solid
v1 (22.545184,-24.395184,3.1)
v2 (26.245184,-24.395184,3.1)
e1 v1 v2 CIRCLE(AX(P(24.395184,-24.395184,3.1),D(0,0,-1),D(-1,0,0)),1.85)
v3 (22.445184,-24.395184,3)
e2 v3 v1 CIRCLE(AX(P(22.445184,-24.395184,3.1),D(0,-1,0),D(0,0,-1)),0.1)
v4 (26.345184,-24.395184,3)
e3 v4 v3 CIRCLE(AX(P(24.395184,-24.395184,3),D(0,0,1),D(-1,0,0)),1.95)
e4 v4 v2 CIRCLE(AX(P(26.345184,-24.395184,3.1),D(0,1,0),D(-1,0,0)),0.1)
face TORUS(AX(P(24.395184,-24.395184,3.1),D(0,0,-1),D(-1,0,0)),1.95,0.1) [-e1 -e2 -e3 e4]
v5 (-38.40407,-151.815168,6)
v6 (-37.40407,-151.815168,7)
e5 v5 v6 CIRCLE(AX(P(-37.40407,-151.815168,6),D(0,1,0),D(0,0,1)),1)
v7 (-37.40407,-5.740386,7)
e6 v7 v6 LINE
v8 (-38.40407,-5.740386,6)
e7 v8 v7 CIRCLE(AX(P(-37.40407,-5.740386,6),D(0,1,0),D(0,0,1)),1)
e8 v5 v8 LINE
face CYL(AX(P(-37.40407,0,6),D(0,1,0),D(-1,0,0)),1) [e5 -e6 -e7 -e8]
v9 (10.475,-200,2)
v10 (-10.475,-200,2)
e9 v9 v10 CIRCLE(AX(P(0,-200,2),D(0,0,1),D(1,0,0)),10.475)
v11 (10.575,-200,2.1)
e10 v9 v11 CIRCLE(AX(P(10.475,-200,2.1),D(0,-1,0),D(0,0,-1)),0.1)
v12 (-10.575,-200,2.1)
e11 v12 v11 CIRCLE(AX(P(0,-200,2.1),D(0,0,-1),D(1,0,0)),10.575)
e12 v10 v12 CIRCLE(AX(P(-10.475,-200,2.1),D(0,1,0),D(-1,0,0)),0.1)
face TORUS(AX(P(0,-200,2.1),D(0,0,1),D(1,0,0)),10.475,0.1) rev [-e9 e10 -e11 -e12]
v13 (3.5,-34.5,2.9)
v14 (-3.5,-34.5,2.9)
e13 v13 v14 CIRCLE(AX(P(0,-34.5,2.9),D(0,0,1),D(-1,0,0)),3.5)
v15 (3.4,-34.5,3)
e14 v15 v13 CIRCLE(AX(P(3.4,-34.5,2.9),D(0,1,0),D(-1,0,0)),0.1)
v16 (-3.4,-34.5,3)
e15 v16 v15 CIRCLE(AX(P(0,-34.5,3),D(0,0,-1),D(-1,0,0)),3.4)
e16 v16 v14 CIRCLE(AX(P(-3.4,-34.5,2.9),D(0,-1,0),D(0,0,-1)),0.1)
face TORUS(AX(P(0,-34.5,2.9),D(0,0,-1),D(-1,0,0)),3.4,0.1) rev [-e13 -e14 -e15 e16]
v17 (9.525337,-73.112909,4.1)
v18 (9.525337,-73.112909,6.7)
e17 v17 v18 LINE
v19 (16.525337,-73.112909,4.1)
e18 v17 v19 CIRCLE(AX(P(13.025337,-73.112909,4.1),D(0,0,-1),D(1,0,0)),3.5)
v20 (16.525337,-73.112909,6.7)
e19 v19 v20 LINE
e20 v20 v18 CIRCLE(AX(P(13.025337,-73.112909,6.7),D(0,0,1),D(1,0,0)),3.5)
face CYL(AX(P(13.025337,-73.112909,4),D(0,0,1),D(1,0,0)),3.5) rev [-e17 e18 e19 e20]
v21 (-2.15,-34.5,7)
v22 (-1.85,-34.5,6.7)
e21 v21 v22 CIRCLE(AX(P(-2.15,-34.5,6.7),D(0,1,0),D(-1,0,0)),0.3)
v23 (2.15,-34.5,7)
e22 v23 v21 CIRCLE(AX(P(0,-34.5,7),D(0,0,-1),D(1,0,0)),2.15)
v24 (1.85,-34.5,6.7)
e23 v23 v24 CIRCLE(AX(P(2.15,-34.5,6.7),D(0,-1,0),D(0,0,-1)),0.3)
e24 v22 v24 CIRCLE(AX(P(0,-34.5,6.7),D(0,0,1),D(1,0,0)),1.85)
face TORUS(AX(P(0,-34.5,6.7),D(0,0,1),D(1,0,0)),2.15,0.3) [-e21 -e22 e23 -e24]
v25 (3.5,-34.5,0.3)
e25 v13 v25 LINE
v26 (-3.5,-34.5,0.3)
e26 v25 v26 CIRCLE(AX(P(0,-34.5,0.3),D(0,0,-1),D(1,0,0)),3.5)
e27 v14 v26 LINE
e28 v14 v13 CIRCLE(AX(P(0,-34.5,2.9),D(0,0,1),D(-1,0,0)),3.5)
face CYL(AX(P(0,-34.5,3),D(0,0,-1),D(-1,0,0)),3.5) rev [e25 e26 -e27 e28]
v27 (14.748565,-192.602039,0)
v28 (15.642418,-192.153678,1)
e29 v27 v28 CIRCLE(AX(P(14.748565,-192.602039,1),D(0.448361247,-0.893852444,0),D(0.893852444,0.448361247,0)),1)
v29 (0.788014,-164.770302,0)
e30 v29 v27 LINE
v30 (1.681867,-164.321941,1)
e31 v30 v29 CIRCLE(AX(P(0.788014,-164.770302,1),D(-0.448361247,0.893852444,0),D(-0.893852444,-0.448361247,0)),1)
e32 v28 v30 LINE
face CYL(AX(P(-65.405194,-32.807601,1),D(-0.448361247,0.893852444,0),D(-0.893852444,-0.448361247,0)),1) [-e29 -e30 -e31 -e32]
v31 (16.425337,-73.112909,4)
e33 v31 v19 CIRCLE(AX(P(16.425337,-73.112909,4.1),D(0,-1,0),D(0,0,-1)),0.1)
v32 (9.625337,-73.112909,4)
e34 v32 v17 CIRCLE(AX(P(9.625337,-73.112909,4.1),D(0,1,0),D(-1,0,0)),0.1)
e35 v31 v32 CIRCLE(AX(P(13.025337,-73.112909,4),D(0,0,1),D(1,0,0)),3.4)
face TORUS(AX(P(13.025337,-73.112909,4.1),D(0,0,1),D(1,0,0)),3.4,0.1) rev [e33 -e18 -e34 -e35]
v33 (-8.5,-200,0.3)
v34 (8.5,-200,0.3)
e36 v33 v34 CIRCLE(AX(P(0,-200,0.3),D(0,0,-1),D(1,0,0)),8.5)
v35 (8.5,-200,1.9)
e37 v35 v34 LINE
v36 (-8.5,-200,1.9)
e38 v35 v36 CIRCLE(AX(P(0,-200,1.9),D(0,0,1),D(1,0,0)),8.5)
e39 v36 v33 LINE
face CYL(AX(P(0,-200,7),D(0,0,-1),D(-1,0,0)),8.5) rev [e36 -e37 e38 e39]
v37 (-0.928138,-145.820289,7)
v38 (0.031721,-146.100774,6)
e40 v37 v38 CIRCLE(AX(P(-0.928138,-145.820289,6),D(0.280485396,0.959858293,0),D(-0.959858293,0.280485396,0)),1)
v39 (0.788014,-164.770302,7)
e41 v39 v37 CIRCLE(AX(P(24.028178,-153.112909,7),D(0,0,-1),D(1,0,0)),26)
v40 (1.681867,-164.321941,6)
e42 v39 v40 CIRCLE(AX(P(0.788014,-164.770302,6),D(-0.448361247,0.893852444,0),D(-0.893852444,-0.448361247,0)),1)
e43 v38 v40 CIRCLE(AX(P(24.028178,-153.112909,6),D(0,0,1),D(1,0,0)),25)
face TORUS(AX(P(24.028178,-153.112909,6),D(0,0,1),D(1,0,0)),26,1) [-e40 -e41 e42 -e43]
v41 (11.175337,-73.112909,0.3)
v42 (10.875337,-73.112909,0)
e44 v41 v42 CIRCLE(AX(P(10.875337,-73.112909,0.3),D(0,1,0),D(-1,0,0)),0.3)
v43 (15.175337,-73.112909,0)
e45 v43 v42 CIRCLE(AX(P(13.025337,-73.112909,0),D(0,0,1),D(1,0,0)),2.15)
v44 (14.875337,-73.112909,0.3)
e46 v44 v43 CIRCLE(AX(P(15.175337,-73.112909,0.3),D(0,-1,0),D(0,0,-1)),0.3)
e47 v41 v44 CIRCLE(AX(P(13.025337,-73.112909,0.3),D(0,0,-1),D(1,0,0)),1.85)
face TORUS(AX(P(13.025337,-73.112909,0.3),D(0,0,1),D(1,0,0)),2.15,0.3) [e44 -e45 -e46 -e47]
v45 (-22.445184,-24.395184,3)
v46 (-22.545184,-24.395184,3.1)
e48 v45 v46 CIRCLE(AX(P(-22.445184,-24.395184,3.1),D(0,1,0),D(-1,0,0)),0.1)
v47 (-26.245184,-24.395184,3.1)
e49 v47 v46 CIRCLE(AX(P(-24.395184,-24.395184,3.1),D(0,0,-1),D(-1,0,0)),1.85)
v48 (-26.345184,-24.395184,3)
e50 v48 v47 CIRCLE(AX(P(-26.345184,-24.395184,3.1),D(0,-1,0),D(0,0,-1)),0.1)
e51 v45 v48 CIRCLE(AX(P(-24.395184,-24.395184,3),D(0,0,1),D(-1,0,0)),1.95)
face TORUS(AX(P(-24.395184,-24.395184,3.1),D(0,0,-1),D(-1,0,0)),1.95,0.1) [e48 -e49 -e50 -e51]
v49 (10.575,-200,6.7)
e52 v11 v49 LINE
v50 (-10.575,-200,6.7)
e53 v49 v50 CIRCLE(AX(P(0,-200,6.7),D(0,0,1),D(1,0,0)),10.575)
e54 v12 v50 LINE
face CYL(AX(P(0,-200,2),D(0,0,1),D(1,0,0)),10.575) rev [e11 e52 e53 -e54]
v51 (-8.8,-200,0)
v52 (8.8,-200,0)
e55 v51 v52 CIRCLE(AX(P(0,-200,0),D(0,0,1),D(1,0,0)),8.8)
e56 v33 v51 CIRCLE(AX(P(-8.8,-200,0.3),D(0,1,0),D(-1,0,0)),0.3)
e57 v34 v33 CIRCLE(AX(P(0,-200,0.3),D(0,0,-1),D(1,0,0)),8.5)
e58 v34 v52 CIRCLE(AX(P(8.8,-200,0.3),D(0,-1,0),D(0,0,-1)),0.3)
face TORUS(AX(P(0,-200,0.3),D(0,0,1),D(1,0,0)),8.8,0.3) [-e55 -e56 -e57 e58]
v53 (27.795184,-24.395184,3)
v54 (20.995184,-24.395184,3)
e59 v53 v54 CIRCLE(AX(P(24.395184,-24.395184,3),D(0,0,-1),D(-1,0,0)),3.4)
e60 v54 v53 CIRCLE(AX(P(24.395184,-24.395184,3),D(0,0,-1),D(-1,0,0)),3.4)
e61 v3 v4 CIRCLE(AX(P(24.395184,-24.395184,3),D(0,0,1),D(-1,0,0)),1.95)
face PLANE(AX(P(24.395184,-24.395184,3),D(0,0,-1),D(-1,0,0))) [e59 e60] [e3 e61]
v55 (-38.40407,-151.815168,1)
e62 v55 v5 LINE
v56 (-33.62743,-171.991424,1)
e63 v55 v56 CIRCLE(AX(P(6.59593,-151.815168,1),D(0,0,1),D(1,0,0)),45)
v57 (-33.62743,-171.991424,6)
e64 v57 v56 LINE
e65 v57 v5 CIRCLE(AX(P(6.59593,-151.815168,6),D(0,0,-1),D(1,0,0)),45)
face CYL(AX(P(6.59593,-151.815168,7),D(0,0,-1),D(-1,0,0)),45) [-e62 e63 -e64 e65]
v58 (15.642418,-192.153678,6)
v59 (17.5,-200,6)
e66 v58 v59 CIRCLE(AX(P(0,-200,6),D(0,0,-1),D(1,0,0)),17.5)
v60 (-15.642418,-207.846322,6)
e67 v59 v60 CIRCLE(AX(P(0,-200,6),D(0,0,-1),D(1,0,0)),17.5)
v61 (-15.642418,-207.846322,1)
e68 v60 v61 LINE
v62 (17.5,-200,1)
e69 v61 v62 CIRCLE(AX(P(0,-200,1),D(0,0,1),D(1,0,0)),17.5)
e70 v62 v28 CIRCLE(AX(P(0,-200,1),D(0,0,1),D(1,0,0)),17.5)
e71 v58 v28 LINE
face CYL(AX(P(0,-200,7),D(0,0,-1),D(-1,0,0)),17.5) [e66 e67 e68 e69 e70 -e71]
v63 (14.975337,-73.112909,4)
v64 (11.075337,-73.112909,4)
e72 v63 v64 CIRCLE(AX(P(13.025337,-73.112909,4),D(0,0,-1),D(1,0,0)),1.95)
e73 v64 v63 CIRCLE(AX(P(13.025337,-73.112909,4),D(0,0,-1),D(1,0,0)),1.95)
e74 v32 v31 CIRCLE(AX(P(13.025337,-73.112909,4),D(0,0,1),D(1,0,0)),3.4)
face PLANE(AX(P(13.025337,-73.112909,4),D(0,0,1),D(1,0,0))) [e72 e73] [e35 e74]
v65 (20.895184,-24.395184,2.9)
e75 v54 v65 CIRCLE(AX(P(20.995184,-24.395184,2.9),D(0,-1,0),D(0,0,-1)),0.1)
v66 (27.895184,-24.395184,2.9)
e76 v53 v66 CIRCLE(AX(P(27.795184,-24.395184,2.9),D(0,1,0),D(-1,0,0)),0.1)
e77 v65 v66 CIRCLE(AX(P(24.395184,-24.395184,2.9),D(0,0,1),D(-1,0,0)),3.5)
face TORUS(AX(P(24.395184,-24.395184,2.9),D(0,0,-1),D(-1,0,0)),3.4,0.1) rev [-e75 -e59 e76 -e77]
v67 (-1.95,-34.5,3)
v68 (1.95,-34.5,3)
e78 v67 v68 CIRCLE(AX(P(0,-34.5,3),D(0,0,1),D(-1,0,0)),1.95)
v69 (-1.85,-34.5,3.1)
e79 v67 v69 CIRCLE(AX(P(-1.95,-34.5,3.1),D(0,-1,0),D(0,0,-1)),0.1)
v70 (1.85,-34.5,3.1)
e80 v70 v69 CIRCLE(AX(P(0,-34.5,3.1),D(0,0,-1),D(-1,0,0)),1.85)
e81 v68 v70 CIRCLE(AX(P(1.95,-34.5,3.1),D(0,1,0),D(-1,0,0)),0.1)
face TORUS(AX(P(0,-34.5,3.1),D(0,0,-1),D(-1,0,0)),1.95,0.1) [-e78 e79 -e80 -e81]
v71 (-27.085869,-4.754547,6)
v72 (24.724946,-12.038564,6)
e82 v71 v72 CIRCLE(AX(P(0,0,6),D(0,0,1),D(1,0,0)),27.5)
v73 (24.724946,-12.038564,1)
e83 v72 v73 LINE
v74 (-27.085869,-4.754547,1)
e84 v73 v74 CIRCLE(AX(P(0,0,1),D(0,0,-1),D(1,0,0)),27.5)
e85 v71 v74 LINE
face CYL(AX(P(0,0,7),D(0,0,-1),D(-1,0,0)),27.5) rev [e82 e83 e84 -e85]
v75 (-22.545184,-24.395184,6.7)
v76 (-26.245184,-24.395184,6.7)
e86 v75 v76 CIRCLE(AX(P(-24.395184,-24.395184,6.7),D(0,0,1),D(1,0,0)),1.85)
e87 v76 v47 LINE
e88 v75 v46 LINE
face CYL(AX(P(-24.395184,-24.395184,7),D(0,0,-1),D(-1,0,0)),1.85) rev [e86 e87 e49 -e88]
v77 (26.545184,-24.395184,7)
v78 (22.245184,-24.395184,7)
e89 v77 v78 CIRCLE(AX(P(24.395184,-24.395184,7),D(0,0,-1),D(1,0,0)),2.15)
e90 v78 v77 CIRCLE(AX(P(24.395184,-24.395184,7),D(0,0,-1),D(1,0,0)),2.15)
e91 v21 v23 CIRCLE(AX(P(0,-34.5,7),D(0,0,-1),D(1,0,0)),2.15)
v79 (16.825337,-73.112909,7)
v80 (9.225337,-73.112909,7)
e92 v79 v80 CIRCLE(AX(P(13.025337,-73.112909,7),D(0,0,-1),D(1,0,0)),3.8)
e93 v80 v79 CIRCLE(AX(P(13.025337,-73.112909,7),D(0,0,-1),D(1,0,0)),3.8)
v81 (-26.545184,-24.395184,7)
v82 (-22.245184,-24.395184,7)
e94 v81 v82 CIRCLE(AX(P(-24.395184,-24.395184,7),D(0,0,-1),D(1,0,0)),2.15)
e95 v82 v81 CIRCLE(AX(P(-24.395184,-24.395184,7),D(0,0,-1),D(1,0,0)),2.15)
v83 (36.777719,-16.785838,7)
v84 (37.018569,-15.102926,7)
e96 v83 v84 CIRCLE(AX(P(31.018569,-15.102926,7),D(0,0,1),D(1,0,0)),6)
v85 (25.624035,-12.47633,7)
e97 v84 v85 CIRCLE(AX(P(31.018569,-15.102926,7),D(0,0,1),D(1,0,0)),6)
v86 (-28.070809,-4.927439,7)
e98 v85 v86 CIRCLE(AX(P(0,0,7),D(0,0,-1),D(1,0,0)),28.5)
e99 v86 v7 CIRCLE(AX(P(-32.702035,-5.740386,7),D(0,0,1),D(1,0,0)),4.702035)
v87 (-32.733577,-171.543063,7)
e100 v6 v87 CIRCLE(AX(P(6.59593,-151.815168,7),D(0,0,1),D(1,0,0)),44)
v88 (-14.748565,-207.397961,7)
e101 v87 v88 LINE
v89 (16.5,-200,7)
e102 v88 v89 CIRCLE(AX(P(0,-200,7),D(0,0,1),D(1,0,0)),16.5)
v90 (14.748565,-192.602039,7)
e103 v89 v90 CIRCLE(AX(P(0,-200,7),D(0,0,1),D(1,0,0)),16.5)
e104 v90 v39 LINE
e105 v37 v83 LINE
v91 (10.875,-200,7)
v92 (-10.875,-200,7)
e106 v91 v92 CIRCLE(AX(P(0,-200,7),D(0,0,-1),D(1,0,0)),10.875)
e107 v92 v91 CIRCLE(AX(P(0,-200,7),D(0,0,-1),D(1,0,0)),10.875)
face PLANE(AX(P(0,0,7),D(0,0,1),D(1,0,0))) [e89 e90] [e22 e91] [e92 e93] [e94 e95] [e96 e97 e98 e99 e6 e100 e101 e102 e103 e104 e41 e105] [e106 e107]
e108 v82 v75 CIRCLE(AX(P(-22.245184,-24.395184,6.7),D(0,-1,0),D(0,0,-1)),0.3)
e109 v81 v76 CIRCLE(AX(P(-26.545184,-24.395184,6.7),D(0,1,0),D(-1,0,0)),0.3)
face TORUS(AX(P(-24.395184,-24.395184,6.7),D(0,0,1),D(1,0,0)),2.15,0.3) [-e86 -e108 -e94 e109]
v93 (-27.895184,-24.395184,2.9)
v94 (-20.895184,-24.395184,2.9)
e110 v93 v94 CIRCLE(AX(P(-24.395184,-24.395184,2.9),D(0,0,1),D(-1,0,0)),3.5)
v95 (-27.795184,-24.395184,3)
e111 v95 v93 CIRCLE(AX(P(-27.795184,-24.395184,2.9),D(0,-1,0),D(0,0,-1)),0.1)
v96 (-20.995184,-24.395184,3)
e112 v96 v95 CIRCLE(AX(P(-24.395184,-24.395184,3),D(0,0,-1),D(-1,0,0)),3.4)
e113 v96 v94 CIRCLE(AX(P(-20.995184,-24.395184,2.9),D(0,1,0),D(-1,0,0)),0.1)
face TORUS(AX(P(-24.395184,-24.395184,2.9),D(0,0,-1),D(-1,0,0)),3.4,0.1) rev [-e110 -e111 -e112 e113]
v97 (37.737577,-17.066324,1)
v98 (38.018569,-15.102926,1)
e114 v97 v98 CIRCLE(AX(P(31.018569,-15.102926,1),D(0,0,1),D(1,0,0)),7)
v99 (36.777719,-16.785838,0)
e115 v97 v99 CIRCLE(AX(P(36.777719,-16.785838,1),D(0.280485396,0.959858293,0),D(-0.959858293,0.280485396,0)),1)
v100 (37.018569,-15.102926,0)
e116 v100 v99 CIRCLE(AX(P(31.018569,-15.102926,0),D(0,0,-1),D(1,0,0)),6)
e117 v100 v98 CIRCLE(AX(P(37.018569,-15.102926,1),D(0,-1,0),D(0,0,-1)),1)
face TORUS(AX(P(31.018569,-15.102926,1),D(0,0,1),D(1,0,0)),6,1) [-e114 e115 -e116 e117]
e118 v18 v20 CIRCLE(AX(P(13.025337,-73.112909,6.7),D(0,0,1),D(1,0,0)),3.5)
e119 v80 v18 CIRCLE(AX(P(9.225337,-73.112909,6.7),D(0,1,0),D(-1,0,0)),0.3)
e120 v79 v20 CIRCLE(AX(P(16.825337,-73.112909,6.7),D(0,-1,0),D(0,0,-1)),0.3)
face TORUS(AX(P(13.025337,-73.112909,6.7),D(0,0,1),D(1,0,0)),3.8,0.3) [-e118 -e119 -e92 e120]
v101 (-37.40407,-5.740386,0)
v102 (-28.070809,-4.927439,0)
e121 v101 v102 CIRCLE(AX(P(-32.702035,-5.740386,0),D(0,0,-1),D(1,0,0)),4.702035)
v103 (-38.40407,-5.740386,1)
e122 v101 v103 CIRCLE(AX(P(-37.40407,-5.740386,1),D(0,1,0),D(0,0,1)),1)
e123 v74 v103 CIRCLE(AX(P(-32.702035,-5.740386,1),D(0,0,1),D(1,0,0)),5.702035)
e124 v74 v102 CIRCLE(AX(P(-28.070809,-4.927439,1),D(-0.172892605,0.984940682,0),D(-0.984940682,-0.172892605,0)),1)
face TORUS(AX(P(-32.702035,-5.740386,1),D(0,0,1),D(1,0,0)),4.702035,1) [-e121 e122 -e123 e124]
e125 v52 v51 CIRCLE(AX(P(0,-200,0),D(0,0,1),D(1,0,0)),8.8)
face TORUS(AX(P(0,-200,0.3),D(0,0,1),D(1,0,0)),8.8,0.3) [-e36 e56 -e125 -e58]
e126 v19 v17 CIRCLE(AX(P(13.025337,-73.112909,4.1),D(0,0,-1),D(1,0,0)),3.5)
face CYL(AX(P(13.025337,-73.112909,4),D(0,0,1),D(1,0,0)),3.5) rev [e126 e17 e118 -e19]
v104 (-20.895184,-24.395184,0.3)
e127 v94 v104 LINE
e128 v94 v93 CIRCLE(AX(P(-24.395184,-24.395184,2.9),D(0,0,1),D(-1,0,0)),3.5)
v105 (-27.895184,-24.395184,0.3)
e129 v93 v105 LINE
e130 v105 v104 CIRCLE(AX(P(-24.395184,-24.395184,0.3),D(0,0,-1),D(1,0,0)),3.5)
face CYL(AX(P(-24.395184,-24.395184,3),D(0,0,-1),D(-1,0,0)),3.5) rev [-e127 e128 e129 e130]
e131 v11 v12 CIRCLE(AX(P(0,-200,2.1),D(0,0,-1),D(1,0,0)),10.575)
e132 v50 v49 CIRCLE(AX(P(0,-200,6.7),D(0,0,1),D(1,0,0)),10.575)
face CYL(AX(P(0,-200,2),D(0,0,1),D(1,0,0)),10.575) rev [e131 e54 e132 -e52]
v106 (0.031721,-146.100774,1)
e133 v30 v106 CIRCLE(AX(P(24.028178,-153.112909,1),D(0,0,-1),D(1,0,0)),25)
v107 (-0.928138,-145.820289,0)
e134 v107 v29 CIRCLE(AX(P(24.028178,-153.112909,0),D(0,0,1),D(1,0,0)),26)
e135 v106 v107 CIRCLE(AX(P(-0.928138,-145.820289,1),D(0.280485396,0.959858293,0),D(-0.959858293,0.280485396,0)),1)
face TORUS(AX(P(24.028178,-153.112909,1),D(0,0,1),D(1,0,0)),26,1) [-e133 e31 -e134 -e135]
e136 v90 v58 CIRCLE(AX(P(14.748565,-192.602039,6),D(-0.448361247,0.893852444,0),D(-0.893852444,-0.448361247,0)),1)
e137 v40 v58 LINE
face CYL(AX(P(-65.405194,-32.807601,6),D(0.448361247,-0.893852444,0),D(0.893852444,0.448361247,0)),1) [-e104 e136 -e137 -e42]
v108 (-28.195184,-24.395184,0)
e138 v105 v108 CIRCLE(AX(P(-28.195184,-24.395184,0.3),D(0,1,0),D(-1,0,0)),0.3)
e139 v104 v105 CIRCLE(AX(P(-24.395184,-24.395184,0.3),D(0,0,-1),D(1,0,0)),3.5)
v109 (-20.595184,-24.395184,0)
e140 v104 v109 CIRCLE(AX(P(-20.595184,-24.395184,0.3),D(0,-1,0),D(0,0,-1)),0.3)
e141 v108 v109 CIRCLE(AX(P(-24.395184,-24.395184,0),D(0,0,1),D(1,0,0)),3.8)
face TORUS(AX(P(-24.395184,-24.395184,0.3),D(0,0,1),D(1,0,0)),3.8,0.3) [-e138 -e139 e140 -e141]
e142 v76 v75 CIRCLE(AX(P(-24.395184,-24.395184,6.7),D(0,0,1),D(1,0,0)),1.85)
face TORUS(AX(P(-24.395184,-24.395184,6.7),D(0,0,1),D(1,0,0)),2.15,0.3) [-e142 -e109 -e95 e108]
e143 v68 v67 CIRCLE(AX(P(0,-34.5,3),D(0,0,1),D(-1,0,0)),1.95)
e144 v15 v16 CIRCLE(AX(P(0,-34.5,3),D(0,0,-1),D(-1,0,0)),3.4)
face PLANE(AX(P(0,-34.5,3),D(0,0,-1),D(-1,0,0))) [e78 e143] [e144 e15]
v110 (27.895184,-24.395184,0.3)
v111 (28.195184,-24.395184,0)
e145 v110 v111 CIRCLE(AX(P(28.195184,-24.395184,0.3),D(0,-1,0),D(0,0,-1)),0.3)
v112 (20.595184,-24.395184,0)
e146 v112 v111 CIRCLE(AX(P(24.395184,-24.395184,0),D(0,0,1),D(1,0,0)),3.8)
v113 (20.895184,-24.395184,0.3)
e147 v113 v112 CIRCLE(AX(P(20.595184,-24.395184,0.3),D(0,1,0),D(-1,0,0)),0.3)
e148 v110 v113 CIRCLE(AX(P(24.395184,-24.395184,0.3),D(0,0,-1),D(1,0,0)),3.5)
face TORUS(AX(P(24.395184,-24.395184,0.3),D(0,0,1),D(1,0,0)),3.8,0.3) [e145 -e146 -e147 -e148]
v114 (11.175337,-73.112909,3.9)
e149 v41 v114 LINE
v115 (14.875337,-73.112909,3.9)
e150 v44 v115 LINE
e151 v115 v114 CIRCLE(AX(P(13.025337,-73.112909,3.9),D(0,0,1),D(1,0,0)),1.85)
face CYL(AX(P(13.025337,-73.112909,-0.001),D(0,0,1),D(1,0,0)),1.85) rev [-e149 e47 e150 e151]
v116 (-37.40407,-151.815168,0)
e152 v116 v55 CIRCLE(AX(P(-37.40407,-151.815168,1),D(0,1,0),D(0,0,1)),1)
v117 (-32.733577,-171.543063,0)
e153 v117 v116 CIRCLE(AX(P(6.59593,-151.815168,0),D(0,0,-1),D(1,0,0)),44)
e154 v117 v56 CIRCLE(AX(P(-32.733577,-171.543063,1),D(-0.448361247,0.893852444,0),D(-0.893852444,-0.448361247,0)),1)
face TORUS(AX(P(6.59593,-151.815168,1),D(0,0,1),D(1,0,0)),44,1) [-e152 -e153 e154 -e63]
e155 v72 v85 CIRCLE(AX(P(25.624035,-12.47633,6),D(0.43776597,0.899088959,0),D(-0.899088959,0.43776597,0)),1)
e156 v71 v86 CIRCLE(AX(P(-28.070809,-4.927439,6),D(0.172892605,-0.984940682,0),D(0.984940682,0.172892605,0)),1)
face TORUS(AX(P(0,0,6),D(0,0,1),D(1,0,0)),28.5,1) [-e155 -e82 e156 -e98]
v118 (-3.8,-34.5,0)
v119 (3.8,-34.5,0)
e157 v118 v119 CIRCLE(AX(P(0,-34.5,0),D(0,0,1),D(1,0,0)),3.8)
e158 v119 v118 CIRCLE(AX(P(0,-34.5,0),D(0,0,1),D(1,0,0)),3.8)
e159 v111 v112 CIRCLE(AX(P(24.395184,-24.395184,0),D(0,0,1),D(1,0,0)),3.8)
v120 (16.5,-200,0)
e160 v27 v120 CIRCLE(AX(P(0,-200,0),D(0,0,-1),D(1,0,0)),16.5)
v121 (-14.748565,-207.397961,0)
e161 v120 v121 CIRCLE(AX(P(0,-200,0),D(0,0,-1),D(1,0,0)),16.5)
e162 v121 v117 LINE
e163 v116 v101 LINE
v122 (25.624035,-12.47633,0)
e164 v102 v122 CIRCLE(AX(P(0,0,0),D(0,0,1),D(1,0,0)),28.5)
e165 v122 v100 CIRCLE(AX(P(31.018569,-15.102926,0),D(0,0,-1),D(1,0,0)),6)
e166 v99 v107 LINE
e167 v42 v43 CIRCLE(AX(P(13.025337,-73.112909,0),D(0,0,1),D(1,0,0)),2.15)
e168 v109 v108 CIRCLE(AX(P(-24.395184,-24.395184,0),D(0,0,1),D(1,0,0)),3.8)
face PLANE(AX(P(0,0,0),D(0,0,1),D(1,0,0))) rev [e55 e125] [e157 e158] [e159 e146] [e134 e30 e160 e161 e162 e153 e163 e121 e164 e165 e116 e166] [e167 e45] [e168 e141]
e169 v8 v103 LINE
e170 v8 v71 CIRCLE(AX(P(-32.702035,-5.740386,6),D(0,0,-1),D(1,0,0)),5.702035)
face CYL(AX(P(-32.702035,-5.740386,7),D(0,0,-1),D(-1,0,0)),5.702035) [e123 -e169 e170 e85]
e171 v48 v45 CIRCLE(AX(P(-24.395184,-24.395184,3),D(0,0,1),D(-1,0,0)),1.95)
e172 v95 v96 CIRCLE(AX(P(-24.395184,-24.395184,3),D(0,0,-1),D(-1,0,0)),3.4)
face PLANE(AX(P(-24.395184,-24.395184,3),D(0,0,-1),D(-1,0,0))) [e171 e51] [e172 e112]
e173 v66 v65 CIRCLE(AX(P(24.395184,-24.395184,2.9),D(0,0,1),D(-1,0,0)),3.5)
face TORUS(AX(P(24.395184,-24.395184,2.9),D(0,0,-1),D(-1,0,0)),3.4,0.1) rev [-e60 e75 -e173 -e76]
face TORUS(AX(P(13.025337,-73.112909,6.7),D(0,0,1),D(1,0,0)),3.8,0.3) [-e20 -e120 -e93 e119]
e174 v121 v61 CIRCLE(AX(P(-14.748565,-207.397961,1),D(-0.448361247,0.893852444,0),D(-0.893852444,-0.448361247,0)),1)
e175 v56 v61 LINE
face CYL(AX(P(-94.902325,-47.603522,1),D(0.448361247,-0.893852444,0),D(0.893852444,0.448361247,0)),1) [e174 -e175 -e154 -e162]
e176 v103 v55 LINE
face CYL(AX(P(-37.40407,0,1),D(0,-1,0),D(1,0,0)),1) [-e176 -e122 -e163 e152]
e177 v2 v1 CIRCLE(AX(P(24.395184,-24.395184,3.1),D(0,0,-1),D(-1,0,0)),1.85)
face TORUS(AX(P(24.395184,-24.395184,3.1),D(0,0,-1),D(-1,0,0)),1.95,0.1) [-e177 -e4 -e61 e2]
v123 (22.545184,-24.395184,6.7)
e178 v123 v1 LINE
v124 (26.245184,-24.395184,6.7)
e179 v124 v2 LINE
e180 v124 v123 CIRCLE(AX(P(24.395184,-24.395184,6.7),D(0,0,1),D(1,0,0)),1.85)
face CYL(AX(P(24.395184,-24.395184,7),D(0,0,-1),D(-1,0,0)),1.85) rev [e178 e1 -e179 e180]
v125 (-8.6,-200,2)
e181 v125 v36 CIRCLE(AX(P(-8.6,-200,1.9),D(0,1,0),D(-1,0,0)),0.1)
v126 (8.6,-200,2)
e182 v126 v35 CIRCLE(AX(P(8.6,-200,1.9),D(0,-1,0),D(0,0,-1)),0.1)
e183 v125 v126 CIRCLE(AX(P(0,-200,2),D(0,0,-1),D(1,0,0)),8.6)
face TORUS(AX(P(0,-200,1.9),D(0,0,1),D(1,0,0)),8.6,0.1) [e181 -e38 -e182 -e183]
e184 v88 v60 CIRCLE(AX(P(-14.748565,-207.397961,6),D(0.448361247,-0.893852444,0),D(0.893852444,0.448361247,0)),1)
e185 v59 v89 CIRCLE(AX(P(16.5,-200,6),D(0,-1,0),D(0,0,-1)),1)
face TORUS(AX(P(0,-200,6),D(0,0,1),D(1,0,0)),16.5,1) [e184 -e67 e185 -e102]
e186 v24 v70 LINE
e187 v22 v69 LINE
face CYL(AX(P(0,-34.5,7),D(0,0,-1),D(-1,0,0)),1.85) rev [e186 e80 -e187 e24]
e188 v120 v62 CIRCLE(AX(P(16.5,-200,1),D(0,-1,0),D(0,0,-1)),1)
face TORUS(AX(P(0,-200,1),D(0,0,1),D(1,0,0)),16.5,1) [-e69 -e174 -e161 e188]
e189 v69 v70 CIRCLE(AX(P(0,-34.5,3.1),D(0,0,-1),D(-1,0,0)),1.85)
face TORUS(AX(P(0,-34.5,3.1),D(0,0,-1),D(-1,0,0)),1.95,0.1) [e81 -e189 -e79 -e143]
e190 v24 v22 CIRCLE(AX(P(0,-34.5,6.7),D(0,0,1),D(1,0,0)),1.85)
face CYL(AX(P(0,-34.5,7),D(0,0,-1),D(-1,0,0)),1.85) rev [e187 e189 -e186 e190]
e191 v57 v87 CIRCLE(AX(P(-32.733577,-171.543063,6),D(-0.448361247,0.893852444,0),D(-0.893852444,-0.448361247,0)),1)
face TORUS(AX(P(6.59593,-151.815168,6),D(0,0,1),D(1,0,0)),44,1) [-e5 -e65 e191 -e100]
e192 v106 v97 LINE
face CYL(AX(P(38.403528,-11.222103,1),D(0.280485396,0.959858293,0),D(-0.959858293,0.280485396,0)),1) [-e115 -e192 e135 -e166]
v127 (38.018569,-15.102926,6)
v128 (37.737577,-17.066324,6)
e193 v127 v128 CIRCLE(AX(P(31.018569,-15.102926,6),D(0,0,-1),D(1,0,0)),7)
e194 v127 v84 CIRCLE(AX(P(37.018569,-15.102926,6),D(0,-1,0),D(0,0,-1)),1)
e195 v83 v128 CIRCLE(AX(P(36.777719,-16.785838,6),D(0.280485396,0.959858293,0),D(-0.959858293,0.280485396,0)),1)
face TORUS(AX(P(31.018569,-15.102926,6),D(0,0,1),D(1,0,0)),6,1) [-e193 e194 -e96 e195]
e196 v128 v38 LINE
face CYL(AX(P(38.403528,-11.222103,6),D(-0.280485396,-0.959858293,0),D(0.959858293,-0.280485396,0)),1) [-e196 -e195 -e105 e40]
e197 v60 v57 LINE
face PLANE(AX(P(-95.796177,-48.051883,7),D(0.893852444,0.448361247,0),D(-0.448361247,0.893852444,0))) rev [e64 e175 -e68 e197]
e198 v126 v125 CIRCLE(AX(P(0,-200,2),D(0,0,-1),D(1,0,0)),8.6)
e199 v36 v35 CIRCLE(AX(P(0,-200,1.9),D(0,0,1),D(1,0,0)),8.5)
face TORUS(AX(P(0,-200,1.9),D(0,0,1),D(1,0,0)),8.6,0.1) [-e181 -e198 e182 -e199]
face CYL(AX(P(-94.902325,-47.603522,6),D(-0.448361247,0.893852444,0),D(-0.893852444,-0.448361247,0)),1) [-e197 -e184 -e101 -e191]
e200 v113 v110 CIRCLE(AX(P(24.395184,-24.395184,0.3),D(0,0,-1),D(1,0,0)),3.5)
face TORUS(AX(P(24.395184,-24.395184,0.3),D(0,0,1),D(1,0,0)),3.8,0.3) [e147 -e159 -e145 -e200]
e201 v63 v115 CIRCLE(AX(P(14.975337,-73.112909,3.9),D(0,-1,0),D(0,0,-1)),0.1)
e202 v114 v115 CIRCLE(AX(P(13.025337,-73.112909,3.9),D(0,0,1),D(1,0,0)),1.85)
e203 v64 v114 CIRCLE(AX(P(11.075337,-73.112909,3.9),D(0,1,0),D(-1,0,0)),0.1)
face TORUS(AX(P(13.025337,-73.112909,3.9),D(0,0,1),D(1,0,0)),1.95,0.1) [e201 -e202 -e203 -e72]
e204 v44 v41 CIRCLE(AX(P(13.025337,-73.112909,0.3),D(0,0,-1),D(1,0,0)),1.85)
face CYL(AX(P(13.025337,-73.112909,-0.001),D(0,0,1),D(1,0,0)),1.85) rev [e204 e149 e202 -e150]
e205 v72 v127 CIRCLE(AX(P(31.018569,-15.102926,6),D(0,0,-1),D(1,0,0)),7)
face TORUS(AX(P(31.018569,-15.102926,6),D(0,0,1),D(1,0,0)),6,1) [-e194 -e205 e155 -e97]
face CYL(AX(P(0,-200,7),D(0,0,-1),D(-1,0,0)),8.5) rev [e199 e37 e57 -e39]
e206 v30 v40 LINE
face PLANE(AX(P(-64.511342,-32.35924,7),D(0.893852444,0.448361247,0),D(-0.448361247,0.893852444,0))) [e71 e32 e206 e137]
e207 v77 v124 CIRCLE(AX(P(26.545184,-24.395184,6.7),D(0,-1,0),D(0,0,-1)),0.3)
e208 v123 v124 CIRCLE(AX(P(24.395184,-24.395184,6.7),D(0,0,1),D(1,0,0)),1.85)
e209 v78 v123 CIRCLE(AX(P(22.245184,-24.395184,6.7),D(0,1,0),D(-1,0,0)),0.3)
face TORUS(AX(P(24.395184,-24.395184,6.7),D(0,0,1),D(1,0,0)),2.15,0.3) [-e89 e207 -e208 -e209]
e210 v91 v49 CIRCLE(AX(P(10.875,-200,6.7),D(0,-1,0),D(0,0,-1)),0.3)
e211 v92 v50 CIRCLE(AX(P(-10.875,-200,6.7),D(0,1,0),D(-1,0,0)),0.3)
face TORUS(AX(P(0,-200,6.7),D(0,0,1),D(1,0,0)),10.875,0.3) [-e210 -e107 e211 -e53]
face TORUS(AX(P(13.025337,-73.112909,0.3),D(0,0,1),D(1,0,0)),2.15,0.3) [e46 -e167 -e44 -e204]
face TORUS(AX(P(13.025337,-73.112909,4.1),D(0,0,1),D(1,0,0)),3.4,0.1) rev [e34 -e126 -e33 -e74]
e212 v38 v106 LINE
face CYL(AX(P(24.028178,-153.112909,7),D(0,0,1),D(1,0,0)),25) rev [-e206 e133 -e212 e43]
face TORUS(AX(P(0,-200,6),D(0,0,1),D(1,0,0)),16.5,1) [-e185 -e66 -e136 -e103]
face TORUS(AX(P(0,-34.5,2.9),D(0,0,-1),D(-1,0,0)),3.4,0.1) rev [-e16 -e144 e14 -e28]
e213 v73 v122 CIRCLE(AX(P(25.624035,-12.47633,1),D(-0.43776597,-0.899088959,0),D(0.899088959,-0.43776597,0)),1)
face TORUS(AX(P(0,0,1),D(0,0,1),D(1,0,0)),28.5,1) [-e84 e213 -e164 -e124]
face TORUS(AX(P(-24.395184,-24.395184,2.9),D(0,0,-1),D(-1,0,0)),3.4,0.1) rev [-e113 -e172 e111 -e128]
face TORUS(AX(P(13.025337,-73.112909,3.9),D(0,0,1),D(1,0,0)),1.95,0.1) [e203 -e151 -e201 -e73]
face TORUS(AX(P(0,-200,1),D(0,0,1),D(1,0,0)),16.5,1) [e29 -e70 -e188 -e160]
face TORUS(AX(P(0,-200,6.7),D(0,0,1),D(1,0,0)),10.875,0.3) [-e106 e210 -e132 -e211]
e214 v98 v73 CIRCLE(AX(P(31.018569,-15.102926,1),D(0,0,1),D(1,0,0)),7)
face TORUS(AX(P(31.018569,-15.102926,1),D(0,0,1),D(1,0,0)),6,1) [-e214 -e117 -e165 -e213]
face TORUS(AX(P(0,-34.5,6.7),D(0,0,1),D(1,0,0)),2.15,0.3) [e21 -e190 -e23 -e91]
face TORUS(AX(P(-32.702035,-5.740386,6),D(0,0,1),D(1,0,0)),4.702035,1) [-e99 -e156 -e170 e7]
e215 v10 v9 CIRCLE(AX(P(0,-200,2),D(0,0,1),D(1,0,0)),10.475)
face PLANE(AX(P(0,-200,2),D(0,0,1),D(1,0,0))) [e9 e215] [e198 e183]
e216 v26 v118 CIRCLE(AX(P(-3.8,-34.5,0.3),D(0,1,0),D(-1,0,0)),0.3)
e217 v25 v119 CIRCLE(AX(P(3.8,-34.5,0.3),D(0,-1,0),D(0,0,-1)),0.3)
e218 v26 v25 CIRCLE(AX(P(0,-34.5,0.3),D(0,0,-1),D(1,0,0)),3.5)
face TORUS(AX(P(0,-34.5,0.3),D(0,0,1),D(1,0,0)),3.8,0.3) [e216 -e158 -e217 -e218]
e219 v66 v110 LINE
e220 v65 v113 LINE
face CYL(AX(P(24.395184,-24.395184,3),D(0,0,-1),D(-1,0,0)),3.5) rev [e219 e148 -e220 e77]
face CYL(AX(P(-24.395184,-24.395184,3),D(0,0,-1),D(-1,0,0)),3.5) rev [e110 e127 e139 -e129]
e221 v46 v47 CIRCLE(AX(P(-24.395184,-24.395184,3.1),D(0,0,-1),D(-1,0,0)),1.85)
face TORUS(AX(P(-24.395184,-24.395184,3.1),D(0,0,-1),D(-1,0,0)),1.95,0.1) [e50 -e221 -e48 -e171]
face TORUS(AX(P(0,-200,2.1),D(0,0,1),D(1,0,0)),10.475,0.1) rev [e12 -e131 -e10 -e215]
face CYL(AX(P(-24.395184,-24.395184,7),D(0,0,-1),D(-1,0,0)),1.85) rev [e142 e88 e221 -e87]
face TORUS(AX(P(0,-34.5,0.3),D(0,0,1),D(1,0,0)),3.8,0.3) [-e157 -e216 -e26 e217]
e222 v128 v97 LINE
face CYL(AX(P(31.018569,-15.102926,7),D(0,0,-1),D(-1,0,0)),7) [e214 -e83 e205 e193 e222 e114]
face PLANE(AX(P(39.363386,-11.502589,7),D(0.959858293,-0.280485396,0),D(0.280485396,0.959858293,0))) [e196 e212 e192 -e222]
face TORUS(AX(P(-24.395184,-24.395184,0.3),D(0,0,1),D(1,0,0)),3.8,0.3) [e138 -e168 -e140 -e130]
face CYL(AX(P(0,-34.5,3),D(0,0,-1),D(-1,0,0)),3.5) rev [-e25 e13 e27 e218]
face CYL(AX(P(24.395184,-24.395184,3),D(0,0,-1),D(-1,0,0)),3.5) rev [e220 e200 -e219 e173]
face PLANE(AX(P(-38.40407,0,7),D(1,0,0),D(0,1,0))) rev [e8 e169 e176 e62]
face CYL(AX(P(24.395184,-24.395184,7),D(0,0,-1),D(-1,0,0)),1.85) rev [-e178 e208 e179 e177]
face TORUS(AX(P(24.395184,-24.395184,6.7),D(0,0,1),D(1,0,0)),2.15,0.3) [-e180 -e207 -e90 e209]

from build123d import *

# Parameters (mm, degrees)
SKETCH1_R           = 1.85
SKETCH1_R_2         = 8.5
BOSS_EXTRUDE1_DEPTH = 7
SKETCH2_R           = 10.575
CUT_EXTRUDE1_DEPTH  = 5
FILLET1_R           = 25
FILLET2_R           = 45
CUT_EXTRUDE2_REACH  = 222.975
SKETCH3_R           = 1.85
SKETCH8_R           = 3.5
CUT_EXTRUDE7_DEPTH  = 3
SKETCH9_R           = 3.5
CUT_EXTRUDE8_DEPTH  = 3
FILLET3_R           = 1
FILLET4_R           = 0.3
FILLET5_R           = 0.1


with BuildPart() as part:
    # Sketch1 → Boss-Extrude1 (new body)
    with BuildSketch(Plane.XY):
        with BuildLine():
            Line((-38.404069543, -5.740386291), (-38.404069543, -162.468720195))
            Line((-38.404069543, -162.468720195), (-15.642417773, -207.846321828))
            ThreePointArc((-15.642417773, -207.846321828), (7.846321828, -215.642417773), (15.642417773, -192.153678172))
            Line((15.642417773, -192.153678172), (-2.725328205, -155.535761851))
            Line((-2.725328205, -155.535761851), (37.73757713, -17.066323725))
            ThreePointArc((37.73757713, -17.066323725), (33.541430495, -8.573364688), (24.724946368, -12.038564163))
            ThreePointArc((24.724946368, -12.038564163), (-3.828539726, -27.232192045), (-27.085868755, -4.754546644))
            ThreePointArc((-27.085868755, -4.754546644), (-33.1968209, -0.059859271), (-38.404069543, -5.740386291))
        make_face()
        with Locations((0, -34.5)):
            Circle(SKETCH1_R, mode=Mode.SUBTRACT)
        with Locations((24.395183951, -24.395183951)):
            Circle(SKETCH1_R, mode=Mode.SUBTRACT)
        with Locations((-24.395183951, -24.395183951)):
            Circle(SKETCH1_R, mode=Mode.SUBTRACT)
        with Locations((0, -200)):
            Circle(SKETCH1_R_2, mode=Mode.SUBTRACT)
    extrude(amount=BOSS_EXTRUDE1_DEPTH)

    # Sketch2 → Cut-Extrude1 (cut)
    with BuildSketch(Plane.XY.offset(7)):
        with Locations((0, -200)):
            Circle(SKETCH2_R)
    extrude(amount=-CUT_EXTRUDE1_DEPTH, mode=Mode.SUBTRACT)

    # Fillet1
    fillet1_edges = [part.edges().sort_by_distance(p)[0] for p in [
        (-2.725328205, -155.535761851, 3.5),
    ]]
    fillet(fillet1_edges, radius=FILLET1_R)

    # Fillet2
    fillet2_edges = [part.edges().sort_by_distance(p)[0] for p in [
        (-38.404069543, -162.468720195, 3.5),
    ]]
    fillet(fillet2_edges, radius=FILLET2_R)

    # Sketch3 → Cut-Extrude2 (cut, up to next)
    with BuildSketch(Plane.XY.offset(7), mode=Mode.PRIVATE) as cut_extrude2_sk1:
        with Locations((13.025336819, -73.112909397)):
            Circle(SKETCH3_R)
    cut_extrude2_tool1 = extrude(cut_extrude2_sk1.sketch, amount=-CUT_EXTRUDE2_REACH, mode=Mode.PRIVATE) & part.part
    add(cut_extrude2_tool1.solids().sort_by_distance((13.025337, -73.112909, 7))[0], mode=Mode.SUBTRACT)

    # Sketch8 → Cut-Extrude7 (cut)
    with BuildSketch(Plane(origin=(0, 0, 0), x_dir=(-1, 0, 0), z_dir=(0, 0, -1))):
        with Locations((0, -34.5)):
            Circle(SKETCH8_R)
        with Locations((-24.395183951, -24.395183951)):
            Circle(SKETCH8_R)
        with Locations((24.395183951, -24.395183951)):
            Circle(SKETCH8_R)
    extrude(amount=-CUT_EXTRUDE7_DEPTH, mode=Mode.SUBTRACT)

    # Sketch9 → Cut-Extrude8 (cut)
    with BuildSketch(Plane.XY.offset(7)):
        with Locations((13.025336819, -73.112909397)):
            Circle(SKETCH9_R)
    extrude(amount=-CUT_EXTRUDE8_DEPTH, mode=Mode.SUBTRACT)

    # Fillet3
    fillet3_edges = [part.edges().sort_by_distance(p)[0] for p in [
        (7.846321828, -215.642417773, 0),
        (-38.404069543, -78.777777075, 0),
        (-33.1968209, -0.059859271, 0),
        (-3.828539726, -27.232192045, 0),
        (33.541430495, -8.573364688, 0),
        (18.884648871, -81.583549106, 0),
        (18.884648871, -81.583549106, 7),
        (33.541430495, -8.573364688, 7),
        (-3.828539726, -27.232192045, 7),
        (-33.1968209, -0.059859271, 7),
        (8.662142301, -178.237809376, 0),
        (8.662142301, -178.237809376, 7),
        (-0.869929821, -155.367733163, 0),
        (-38.404069543, -78.777777075, 7),
        (-0.869929821, -155.367733163, 7),
        (-24.634923651, -189.918872908, 0),
        (-24.634923651, -189.918872908, 7),
        (-37.19362994, -162.182153935, 0),
        (-37.19362994, -162.182153935, 7),
        (7.846321828, -215.642417773, 7),
    ]]
    fillet(fillet3_edges, radius=FILLET3_R)

    # Fillet4
    fillet4_edges = [part.edges().sort_by_distance(p)[0] for p in [
        (-26.245183951, -24.395183951, 7),
        (22.545183951, -24.395183951, 7),
        (-8.5, -200, 0),
        (-1.85, -34.5, 7),
        (-10.575, -200, 7),
        (11.175336819, -73.112909397, 0),
        (3.5, -34.5, 0),
        (27.895183951, -24.395183951, 0),
        (-20.895183951, -24.395183951, 0),
        (9.525336819, -73.112909397, 7),
    ]]
    fillet(fillet4_edges, radius=FILLET4_R)

    # Fillet5
    fillet5_edges = [part.edges().sort_by_distance(p)[0] for p in [
        (-10.575, -200, 2),
        (-8.5, -200, 2),
        (3.5, -34.5, 3),
        (-1.85, -34.5, 3),
        (27.895183951, -24.395183951, 3),
        (22.545183951, -24.395183951, 3),
        (-20.895183951, -24.395183951, 3),
        (-26.245183951, -24.395183951, 3),
        (9.525336819, -73.112909397, 4),
        (11.175336819, -73.112909397, 4),
    ]]
    fillet(fillet5_edges, radius=FILLET5_R)


solid = part.part
